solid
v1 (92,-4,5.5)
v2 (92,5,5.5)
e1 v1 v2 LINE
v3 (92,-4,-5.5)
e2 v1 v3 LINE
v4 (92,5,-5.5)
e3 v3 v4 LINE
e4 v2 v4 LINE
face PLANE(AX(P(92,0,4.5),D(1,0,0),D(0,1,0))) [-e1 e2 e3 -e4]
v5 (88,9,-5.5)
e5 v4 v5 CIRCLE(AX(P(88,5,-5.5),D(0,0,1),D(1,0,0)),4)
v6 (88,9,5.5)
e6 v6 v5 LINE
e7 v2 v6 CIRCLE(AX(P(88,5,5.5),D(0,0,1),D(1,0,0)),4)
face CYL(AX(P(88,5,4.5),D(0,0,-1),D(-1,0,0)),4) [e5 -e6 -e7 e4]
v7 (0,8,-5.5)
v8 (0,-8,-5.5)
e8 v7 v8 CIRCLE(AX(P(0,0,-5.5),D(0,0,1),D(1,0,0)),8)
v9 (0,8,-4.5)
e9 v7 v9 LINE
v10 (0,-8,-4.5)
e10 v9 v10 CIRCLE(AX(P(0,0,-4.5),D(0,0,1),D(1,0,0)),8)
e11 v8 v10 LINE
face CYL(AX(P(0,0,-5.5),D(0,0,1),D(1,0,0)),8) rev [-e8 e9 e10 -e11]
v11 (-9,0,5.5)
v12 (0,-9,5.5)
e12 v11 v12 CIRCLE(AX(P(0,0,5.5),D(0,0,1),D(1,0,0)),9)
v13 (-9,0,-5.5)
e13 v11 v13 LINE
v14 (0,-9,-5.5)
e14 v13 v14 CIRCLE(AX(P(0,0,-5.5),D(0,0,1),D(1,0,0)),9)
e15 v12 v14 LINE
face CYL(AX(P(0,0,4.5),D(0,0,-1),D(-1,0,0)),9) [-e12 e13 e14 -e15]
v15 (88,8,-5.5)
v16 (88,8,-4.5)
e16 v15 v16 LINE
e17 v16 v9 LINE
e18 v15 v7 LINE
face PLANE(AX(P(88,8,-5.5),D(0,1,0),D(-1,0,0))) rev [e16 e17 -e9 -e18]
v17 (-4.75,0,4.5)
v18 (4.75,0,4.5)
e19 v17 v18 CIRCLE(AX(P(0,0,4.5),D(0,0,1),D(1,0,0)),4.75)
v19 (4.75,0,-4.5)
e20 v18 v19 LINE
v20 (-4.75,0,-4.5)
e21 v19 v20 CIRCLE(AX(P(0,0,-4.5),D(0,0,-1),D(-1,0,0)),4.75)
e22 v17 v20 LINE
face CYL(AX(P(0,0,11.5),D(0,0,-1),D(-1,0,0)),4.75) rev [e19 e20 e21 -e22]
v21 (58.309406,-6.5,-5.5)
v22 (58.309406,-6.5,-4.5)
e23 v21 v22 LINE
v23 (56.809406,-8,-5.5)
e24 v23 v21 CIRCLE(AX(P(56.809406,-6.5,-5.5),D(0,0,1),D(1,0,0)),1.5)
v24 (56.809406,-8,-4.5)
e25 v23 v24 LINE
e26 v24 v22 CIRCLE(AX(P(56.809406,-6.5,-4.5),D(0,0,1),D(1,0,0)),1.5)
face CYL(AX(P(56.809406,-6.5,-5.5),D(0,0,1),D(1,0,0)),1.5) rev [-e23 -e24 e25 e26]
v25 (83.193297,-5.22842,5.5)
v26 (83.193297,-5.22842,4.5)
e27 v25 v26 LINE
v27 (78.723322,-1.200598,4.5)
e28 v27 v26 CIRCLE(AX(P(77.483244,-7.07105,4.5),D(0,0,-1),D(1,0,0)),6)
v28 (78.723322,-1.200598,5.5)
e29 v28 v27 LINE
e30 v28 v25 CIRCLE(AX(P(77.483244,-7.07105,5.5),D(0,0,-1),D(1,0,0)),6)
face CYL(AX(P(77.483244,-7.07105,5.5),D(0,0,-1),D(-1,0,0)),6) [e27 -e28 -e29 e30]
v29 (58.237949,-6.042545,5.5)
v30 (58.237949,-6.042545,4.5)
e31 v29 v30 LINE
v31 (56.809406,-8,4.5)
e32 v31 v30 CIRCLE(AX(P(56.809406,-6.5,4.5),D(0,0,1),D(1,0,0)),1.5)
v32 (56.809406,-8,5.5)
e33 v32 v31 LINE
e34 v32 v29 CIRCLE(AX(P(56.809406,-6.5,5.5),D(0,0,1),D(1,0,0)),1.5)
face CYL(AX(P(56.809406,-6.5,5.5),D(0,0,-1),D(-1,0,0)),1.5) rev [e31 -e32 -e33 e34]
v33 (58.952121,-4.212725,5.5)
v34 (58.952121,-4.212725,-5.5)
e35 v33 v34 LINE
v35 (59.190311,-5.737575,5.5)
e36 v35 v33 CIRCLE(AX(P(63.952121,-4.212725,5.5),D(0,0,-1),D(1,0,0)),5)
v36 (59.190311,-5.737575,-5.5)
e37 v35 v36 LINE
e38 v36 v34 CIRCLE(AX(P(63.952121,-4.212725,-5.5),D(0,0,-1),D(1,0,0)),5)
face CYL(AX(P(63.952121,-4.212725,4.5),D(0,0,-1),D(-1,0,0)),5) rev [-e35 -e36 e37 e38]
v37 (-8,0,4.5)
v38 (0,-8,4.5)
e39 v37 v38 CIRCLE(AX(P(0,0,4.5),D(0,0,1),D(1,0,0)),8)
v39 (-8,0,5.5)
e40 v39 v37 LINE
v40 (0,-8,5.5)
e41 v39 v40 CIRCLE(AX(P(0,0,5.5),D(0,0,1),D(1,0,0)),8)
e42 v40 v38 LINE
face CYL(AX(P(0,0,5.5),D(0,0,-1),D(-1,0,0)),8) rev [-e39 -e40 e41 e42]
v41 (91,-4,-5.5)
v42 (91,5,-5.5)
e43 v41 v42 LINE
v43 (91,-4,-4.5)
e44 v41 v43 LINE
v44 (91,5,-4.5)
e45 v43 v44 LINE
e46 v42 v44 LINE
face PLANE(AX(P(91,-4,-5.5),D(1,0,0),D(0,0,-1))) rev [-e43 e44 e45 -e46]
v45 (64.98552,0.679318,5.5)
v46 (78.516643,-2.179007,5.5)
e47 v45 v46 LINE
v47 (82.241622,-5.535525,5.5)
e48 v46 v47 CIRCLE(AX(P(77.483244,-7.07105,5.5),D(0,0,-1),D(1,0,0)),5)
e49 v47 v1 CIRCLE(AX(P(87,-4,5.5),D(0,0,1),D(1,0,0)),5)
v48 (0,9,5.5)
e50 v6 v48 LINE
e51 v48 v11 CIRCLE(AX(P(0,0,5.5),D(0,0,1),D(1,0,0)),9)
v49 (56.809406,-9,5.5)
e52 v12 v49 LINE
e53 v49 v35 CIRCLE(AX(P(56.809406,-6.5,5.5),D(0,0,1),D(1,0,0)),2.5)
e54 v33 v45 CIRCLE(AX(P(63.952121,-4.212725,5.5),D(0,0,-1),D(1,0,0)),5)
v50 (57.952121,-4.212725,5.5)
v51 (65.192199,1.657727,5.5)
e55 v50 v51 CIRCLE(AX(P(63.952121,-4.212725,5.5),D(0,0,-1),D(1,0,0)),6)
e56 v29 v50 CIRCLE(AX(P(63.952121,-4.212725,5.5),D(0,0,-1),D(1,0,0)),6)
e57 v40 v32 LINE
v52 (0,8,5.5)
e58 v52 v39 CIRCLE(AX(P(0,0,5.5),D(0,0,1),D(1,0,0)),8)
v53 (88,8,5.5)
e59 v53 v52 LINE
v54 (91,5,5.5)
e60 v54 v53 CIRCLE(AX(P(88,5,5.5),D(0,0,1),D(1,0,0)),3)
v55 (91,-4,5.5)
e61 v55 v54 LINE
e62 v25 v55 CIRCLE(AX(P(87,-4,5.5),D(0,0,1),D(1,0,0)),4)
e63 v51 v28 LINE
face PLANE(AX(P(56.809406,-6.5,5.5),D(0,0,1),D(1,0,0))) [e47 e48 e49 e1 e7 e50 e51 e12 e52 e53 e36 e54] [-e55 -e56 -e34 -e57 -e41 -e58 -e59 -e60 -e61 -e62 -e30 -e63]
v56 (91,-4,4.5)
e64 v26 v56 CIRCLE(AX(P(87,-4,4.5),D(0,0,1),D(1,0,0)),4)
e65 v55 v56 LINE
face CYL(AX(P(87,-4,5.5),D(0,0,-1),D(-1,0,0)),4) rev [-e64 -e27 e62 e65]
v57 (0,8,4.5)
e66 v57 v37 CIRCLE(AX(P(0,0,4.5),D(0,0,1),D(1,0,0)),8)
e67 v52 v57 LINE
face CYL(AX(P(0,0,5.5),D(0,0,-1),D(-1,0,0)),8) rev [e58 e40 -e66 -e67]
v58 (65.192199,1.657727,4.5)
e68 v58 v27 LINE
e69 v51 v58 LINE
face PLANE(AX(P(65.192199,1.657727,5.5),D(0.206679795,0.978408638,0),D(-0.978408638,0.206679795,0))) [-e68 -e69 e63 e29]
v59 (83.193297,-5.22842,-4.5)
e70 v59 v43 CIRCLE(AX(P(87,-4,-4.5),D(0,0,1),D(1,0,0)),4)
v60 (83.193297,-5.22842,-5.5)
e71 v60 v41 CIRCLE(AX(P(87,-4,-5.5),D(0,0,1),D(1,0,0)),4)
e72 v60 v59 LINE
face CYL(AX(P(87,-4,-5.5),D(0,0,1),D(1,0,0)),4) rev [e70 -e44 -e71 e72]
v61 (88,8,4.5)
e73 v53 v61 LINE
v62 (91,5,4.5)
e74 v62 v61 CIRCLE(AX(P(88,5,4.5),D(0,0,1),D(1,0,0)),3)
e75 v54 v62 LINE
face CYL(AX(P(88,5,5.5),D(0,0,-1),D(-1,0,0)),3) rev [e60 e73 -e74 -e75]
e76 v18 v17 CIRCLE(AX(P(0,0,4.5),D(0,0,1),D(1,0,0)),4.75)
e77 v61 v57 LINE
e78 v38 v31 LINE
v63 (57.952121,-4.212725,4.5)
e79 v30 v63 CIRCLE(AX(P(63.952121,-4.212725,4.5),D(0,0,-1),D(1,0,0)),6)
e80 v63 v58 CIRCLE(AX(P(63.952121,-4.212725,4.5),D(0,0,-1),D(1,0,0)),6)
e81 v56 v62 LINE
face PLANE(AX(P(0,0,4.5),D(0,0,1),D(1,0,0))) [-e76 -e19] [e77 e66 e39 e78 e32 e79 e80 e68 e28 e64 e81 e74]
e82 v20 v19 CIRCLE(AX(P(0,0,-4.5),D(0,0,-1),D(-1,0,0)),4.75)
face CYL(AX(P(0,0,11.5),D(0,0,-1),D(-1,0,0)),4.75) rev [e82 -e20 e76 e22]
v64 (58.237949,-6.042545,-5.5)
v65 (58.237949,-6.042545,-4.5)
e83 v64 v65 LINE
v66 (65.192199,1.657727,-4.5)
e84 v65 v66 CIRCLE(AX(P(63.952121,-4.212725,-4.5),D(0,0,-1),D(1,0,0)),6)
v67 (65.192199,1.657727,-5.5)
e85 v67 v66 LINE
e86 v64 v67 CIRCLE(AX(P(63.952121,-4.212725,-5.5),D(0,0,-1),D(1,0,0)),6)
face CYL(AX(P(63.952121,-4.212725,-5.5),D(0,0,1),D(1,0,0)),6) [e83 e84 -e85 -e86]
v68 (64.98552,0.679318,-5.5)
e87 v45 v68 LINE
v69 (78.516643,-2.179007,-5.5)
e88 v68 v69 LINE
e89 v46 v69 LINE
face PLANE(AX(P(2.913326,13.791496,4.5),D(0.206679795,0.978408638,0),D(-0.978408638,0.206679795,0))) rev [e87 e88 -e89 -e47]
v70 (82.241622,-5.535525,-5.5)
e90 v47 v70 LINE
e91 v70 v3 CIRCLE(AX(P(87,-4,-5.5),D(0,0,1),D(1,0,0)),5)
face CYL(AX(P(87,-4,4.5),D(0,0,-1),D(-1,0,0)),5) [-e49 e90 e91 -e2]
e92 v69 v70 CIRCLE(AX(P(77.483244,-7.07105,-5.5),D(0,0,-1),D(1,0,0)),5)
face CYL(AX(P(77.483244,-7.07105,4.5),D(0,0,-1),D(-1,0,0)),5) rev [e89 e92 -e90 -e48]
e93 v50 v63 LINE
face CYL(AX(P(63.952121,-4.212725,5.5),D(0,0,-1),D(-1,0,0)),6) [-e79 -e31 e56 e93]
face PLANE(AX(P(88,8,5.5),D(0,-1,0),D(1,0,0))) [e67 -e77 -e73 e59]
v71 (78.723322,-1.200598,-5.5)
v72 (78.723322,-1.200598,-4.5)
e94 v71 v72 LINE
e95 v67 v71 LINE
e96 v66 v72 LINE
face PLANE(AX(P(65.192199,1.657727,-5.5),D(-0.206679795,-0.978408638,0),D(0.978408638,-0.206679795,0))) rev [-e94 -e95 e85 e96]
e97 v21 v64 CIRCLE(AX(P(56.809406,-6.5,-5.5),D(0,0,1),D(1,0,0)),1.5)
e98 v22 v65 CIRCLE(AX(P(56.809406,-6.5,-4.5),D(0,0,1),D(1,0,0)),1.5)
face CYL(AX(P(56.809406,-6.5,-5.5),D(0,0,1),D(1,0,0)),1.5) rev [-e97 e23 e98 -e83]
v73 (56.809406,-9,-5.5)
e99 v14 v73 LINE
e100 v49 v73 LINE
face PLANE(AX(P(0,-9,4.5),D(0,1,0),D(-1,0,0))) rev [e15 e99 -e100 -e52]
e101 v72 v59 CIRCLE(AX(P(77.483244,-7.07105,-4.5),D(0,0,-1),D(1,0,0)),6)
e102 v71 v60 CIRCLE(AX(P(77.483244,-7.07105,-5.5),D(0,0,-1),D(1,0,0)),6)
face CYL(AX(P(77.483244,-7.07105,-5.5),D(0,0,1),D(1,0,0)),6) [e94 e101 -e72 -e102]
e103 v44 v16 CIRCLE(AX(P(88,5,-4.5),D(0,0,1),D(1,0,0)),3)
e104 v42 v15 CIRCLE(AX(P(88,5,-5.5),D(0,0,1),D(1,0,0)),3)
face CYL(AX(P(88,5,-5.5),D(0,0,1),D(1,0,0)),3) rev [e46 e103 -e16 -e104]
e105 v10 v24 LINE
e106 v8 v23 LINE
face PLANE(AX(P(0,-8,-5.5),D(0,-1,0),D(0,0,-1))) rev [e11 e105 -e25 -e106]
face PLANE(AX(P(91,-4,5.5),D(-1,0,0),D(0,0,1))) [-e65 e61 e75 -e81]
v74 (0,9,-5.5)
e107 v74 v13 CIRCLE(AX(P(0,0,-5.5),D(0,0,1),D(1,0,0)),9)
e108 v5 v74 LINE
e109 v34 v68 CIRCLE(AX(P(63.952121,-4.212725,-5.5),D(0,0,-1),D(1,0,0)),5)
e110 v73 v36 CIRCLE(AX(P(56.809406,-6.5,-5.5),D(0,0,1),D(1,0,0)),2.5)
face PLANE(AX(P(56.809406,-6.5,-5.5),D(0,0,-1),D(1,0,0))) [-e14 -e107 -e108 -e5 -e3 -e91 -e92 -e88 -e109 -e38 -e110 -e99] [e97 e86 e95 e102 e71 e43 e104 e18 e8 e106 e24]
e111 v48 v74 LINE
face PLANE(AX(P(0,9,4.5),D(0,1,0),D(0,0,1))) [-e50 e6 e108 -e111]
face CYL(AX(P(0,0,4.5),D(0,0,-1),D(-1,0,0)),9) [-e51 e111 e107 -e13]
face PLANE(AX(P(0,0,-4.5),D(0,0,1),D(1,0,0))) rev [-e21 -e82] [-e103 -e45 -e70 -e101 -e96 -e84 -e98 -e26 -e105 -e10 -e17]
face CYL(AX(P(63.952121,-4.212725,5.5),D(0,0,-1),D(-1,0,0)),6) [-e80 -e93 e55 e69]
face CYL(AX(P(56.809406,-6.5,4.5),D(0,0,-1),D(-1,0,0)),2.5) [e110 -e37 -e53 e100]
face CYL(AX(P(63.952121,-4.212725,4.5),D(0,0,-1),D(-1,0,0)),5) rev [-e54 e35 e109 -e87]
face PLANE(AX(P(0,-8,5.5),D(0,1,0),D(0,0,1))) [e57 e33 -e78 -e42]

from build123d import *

# Parameters (mm, degrees)
HOOK_BODY_9MM_DEPTH  = 4.5
FACE_START           = 1
FACE_RIM_1MM_DEPTH   = 1
PIVOT_HOLE_SKETCH_R  = 4.75
PIVOT_HOLE_9_5_DEPTH = 16


with BuildPart() as part:
    # Hook Profile Sketch → Hook Body 9mm (new, symmetric)
    with BuildSketch(Plane.XY):
        with BuildLine():
            ThreePointArc((59.190310748, -5.737574987), (60.241407469, -0.861514942), (64.985519507, 0.679318228))
            Line((64.985519507, 0.679318228), (78.516642548, -2.179006643))
            ThreePointArc((78.516642548, -2.179006643), (80.8302907, -3.356581429), (82.241621785, -5.535524915))
            ThreePointArc((82.241621785, -5.535524915), (84.057010413, -8.042129672), (87, -9))
            ThreePointArc((87, -9), (90.535533906, -7.535533906), (92, -4))
            Line((92, -4), (92, 5))
            ThreePointArc((92, 5), (90.828427125, 7.828427125), (88, 9))
            Line((88, 9), (0, 9))
            ThreePointArc((0, 9), (-9, 0), (0, -9))
            Line((0, -9), (56.809405857, -9))
            ThreePointArc((56.809405857, -9), (58.828819452, -7.973760066), (59.190310748, -5.737574987))
        make_face()
    extrude(amount=HOOK_BODY_9MM_DEPTH, both=True)

    # Face Rim Sketch → Face Rim 1mm (add)
    with BuildSketch(Plane.XY.offset(4.5).offset(FACE_START)):
        with BuildLine():
            Line((64.985519507, 0.679318228), (78.516642548, -2.179006643))
            ThreePointArc((78.516642548, -2.179006643), (80.8302907, -3.356581429), (82.241621785, -5.535524915))
            ThreePointArc((82.241621785, -5.535524915), (87.777209408, -8.939225196), (92, -4))
            Line((92, -4), (92, 5))
            ThreePointArc((92, 5), (90.828427125, 7.828427125), (88, 9))
            Line((88, 9), (0, 9))
            ThreePointArc((0, 9), (-9, 0), (0, -9))
            Line((0, -9), (56.809405857, -9))
            ThreePointArc((56.809405857, -9), (58.828819452, -7.973760066), (59.190310748, -5.737574987))
            ThreePointArc((59.190310748, -5.737574987), (60.241407469, -0.861514942), (64.985519507, 0.679318228))
        make_face()
        with BuildLine():
            Line((65.192199302, 1.657726865), (78.723322343, -1.200598005))
            ThreePointArc((78.723322343, -1.200598005), (81.499700126, -2.613687748), (83.193297428, -5.228419932))
            ThreePointArc((83.193297428, -5.228419932), (87.621767526, -7.951380157), (91, -4))
            Line((91, -4), (91, 5))
            ThreePointArc((91, 5), (90.121320344, 7.121320344), (88, 8))
            Line((88, 8), (0, 8))
            ThreePointArc((0, 8), (-8, 0), (0, -8))
            Line((0, -8), (56.809405857, -8))
            ThreePointArc((56.809405857, -8), (58.021054014, -7.38425604), (58.237948791, -6.042544992))
            ThreePointArc((58.237948791, -6.042544992), (59.499264857, -0.191272938), (65.192199302, 1.657726865))
        make_face(mode=Mode.SUBTRACT)
    face_rim_1mm = extrude(amount=-FACE_RIM_1MM_DEPTH)

    # Face Rim Mirror: Face Rim 1mm across plane
    add(face_rim_1mm.mirror(Plane.XY))

    # Pivot Hole Sketch → Pivot Hole Ø9.5 (cut)
    with BuildSketch(Plane(origin=(0, 0, -4.5), x_dir=(-1, 0, 0), z_dir=(0, 0, -1))):
        Circle(PIVOT_HOLE_SKETCH_R)
    extrude(amount=-PIVOT_HOLE_9_5_DEPTH, mode=Mode.SUBTRACT)


solid = part.part
